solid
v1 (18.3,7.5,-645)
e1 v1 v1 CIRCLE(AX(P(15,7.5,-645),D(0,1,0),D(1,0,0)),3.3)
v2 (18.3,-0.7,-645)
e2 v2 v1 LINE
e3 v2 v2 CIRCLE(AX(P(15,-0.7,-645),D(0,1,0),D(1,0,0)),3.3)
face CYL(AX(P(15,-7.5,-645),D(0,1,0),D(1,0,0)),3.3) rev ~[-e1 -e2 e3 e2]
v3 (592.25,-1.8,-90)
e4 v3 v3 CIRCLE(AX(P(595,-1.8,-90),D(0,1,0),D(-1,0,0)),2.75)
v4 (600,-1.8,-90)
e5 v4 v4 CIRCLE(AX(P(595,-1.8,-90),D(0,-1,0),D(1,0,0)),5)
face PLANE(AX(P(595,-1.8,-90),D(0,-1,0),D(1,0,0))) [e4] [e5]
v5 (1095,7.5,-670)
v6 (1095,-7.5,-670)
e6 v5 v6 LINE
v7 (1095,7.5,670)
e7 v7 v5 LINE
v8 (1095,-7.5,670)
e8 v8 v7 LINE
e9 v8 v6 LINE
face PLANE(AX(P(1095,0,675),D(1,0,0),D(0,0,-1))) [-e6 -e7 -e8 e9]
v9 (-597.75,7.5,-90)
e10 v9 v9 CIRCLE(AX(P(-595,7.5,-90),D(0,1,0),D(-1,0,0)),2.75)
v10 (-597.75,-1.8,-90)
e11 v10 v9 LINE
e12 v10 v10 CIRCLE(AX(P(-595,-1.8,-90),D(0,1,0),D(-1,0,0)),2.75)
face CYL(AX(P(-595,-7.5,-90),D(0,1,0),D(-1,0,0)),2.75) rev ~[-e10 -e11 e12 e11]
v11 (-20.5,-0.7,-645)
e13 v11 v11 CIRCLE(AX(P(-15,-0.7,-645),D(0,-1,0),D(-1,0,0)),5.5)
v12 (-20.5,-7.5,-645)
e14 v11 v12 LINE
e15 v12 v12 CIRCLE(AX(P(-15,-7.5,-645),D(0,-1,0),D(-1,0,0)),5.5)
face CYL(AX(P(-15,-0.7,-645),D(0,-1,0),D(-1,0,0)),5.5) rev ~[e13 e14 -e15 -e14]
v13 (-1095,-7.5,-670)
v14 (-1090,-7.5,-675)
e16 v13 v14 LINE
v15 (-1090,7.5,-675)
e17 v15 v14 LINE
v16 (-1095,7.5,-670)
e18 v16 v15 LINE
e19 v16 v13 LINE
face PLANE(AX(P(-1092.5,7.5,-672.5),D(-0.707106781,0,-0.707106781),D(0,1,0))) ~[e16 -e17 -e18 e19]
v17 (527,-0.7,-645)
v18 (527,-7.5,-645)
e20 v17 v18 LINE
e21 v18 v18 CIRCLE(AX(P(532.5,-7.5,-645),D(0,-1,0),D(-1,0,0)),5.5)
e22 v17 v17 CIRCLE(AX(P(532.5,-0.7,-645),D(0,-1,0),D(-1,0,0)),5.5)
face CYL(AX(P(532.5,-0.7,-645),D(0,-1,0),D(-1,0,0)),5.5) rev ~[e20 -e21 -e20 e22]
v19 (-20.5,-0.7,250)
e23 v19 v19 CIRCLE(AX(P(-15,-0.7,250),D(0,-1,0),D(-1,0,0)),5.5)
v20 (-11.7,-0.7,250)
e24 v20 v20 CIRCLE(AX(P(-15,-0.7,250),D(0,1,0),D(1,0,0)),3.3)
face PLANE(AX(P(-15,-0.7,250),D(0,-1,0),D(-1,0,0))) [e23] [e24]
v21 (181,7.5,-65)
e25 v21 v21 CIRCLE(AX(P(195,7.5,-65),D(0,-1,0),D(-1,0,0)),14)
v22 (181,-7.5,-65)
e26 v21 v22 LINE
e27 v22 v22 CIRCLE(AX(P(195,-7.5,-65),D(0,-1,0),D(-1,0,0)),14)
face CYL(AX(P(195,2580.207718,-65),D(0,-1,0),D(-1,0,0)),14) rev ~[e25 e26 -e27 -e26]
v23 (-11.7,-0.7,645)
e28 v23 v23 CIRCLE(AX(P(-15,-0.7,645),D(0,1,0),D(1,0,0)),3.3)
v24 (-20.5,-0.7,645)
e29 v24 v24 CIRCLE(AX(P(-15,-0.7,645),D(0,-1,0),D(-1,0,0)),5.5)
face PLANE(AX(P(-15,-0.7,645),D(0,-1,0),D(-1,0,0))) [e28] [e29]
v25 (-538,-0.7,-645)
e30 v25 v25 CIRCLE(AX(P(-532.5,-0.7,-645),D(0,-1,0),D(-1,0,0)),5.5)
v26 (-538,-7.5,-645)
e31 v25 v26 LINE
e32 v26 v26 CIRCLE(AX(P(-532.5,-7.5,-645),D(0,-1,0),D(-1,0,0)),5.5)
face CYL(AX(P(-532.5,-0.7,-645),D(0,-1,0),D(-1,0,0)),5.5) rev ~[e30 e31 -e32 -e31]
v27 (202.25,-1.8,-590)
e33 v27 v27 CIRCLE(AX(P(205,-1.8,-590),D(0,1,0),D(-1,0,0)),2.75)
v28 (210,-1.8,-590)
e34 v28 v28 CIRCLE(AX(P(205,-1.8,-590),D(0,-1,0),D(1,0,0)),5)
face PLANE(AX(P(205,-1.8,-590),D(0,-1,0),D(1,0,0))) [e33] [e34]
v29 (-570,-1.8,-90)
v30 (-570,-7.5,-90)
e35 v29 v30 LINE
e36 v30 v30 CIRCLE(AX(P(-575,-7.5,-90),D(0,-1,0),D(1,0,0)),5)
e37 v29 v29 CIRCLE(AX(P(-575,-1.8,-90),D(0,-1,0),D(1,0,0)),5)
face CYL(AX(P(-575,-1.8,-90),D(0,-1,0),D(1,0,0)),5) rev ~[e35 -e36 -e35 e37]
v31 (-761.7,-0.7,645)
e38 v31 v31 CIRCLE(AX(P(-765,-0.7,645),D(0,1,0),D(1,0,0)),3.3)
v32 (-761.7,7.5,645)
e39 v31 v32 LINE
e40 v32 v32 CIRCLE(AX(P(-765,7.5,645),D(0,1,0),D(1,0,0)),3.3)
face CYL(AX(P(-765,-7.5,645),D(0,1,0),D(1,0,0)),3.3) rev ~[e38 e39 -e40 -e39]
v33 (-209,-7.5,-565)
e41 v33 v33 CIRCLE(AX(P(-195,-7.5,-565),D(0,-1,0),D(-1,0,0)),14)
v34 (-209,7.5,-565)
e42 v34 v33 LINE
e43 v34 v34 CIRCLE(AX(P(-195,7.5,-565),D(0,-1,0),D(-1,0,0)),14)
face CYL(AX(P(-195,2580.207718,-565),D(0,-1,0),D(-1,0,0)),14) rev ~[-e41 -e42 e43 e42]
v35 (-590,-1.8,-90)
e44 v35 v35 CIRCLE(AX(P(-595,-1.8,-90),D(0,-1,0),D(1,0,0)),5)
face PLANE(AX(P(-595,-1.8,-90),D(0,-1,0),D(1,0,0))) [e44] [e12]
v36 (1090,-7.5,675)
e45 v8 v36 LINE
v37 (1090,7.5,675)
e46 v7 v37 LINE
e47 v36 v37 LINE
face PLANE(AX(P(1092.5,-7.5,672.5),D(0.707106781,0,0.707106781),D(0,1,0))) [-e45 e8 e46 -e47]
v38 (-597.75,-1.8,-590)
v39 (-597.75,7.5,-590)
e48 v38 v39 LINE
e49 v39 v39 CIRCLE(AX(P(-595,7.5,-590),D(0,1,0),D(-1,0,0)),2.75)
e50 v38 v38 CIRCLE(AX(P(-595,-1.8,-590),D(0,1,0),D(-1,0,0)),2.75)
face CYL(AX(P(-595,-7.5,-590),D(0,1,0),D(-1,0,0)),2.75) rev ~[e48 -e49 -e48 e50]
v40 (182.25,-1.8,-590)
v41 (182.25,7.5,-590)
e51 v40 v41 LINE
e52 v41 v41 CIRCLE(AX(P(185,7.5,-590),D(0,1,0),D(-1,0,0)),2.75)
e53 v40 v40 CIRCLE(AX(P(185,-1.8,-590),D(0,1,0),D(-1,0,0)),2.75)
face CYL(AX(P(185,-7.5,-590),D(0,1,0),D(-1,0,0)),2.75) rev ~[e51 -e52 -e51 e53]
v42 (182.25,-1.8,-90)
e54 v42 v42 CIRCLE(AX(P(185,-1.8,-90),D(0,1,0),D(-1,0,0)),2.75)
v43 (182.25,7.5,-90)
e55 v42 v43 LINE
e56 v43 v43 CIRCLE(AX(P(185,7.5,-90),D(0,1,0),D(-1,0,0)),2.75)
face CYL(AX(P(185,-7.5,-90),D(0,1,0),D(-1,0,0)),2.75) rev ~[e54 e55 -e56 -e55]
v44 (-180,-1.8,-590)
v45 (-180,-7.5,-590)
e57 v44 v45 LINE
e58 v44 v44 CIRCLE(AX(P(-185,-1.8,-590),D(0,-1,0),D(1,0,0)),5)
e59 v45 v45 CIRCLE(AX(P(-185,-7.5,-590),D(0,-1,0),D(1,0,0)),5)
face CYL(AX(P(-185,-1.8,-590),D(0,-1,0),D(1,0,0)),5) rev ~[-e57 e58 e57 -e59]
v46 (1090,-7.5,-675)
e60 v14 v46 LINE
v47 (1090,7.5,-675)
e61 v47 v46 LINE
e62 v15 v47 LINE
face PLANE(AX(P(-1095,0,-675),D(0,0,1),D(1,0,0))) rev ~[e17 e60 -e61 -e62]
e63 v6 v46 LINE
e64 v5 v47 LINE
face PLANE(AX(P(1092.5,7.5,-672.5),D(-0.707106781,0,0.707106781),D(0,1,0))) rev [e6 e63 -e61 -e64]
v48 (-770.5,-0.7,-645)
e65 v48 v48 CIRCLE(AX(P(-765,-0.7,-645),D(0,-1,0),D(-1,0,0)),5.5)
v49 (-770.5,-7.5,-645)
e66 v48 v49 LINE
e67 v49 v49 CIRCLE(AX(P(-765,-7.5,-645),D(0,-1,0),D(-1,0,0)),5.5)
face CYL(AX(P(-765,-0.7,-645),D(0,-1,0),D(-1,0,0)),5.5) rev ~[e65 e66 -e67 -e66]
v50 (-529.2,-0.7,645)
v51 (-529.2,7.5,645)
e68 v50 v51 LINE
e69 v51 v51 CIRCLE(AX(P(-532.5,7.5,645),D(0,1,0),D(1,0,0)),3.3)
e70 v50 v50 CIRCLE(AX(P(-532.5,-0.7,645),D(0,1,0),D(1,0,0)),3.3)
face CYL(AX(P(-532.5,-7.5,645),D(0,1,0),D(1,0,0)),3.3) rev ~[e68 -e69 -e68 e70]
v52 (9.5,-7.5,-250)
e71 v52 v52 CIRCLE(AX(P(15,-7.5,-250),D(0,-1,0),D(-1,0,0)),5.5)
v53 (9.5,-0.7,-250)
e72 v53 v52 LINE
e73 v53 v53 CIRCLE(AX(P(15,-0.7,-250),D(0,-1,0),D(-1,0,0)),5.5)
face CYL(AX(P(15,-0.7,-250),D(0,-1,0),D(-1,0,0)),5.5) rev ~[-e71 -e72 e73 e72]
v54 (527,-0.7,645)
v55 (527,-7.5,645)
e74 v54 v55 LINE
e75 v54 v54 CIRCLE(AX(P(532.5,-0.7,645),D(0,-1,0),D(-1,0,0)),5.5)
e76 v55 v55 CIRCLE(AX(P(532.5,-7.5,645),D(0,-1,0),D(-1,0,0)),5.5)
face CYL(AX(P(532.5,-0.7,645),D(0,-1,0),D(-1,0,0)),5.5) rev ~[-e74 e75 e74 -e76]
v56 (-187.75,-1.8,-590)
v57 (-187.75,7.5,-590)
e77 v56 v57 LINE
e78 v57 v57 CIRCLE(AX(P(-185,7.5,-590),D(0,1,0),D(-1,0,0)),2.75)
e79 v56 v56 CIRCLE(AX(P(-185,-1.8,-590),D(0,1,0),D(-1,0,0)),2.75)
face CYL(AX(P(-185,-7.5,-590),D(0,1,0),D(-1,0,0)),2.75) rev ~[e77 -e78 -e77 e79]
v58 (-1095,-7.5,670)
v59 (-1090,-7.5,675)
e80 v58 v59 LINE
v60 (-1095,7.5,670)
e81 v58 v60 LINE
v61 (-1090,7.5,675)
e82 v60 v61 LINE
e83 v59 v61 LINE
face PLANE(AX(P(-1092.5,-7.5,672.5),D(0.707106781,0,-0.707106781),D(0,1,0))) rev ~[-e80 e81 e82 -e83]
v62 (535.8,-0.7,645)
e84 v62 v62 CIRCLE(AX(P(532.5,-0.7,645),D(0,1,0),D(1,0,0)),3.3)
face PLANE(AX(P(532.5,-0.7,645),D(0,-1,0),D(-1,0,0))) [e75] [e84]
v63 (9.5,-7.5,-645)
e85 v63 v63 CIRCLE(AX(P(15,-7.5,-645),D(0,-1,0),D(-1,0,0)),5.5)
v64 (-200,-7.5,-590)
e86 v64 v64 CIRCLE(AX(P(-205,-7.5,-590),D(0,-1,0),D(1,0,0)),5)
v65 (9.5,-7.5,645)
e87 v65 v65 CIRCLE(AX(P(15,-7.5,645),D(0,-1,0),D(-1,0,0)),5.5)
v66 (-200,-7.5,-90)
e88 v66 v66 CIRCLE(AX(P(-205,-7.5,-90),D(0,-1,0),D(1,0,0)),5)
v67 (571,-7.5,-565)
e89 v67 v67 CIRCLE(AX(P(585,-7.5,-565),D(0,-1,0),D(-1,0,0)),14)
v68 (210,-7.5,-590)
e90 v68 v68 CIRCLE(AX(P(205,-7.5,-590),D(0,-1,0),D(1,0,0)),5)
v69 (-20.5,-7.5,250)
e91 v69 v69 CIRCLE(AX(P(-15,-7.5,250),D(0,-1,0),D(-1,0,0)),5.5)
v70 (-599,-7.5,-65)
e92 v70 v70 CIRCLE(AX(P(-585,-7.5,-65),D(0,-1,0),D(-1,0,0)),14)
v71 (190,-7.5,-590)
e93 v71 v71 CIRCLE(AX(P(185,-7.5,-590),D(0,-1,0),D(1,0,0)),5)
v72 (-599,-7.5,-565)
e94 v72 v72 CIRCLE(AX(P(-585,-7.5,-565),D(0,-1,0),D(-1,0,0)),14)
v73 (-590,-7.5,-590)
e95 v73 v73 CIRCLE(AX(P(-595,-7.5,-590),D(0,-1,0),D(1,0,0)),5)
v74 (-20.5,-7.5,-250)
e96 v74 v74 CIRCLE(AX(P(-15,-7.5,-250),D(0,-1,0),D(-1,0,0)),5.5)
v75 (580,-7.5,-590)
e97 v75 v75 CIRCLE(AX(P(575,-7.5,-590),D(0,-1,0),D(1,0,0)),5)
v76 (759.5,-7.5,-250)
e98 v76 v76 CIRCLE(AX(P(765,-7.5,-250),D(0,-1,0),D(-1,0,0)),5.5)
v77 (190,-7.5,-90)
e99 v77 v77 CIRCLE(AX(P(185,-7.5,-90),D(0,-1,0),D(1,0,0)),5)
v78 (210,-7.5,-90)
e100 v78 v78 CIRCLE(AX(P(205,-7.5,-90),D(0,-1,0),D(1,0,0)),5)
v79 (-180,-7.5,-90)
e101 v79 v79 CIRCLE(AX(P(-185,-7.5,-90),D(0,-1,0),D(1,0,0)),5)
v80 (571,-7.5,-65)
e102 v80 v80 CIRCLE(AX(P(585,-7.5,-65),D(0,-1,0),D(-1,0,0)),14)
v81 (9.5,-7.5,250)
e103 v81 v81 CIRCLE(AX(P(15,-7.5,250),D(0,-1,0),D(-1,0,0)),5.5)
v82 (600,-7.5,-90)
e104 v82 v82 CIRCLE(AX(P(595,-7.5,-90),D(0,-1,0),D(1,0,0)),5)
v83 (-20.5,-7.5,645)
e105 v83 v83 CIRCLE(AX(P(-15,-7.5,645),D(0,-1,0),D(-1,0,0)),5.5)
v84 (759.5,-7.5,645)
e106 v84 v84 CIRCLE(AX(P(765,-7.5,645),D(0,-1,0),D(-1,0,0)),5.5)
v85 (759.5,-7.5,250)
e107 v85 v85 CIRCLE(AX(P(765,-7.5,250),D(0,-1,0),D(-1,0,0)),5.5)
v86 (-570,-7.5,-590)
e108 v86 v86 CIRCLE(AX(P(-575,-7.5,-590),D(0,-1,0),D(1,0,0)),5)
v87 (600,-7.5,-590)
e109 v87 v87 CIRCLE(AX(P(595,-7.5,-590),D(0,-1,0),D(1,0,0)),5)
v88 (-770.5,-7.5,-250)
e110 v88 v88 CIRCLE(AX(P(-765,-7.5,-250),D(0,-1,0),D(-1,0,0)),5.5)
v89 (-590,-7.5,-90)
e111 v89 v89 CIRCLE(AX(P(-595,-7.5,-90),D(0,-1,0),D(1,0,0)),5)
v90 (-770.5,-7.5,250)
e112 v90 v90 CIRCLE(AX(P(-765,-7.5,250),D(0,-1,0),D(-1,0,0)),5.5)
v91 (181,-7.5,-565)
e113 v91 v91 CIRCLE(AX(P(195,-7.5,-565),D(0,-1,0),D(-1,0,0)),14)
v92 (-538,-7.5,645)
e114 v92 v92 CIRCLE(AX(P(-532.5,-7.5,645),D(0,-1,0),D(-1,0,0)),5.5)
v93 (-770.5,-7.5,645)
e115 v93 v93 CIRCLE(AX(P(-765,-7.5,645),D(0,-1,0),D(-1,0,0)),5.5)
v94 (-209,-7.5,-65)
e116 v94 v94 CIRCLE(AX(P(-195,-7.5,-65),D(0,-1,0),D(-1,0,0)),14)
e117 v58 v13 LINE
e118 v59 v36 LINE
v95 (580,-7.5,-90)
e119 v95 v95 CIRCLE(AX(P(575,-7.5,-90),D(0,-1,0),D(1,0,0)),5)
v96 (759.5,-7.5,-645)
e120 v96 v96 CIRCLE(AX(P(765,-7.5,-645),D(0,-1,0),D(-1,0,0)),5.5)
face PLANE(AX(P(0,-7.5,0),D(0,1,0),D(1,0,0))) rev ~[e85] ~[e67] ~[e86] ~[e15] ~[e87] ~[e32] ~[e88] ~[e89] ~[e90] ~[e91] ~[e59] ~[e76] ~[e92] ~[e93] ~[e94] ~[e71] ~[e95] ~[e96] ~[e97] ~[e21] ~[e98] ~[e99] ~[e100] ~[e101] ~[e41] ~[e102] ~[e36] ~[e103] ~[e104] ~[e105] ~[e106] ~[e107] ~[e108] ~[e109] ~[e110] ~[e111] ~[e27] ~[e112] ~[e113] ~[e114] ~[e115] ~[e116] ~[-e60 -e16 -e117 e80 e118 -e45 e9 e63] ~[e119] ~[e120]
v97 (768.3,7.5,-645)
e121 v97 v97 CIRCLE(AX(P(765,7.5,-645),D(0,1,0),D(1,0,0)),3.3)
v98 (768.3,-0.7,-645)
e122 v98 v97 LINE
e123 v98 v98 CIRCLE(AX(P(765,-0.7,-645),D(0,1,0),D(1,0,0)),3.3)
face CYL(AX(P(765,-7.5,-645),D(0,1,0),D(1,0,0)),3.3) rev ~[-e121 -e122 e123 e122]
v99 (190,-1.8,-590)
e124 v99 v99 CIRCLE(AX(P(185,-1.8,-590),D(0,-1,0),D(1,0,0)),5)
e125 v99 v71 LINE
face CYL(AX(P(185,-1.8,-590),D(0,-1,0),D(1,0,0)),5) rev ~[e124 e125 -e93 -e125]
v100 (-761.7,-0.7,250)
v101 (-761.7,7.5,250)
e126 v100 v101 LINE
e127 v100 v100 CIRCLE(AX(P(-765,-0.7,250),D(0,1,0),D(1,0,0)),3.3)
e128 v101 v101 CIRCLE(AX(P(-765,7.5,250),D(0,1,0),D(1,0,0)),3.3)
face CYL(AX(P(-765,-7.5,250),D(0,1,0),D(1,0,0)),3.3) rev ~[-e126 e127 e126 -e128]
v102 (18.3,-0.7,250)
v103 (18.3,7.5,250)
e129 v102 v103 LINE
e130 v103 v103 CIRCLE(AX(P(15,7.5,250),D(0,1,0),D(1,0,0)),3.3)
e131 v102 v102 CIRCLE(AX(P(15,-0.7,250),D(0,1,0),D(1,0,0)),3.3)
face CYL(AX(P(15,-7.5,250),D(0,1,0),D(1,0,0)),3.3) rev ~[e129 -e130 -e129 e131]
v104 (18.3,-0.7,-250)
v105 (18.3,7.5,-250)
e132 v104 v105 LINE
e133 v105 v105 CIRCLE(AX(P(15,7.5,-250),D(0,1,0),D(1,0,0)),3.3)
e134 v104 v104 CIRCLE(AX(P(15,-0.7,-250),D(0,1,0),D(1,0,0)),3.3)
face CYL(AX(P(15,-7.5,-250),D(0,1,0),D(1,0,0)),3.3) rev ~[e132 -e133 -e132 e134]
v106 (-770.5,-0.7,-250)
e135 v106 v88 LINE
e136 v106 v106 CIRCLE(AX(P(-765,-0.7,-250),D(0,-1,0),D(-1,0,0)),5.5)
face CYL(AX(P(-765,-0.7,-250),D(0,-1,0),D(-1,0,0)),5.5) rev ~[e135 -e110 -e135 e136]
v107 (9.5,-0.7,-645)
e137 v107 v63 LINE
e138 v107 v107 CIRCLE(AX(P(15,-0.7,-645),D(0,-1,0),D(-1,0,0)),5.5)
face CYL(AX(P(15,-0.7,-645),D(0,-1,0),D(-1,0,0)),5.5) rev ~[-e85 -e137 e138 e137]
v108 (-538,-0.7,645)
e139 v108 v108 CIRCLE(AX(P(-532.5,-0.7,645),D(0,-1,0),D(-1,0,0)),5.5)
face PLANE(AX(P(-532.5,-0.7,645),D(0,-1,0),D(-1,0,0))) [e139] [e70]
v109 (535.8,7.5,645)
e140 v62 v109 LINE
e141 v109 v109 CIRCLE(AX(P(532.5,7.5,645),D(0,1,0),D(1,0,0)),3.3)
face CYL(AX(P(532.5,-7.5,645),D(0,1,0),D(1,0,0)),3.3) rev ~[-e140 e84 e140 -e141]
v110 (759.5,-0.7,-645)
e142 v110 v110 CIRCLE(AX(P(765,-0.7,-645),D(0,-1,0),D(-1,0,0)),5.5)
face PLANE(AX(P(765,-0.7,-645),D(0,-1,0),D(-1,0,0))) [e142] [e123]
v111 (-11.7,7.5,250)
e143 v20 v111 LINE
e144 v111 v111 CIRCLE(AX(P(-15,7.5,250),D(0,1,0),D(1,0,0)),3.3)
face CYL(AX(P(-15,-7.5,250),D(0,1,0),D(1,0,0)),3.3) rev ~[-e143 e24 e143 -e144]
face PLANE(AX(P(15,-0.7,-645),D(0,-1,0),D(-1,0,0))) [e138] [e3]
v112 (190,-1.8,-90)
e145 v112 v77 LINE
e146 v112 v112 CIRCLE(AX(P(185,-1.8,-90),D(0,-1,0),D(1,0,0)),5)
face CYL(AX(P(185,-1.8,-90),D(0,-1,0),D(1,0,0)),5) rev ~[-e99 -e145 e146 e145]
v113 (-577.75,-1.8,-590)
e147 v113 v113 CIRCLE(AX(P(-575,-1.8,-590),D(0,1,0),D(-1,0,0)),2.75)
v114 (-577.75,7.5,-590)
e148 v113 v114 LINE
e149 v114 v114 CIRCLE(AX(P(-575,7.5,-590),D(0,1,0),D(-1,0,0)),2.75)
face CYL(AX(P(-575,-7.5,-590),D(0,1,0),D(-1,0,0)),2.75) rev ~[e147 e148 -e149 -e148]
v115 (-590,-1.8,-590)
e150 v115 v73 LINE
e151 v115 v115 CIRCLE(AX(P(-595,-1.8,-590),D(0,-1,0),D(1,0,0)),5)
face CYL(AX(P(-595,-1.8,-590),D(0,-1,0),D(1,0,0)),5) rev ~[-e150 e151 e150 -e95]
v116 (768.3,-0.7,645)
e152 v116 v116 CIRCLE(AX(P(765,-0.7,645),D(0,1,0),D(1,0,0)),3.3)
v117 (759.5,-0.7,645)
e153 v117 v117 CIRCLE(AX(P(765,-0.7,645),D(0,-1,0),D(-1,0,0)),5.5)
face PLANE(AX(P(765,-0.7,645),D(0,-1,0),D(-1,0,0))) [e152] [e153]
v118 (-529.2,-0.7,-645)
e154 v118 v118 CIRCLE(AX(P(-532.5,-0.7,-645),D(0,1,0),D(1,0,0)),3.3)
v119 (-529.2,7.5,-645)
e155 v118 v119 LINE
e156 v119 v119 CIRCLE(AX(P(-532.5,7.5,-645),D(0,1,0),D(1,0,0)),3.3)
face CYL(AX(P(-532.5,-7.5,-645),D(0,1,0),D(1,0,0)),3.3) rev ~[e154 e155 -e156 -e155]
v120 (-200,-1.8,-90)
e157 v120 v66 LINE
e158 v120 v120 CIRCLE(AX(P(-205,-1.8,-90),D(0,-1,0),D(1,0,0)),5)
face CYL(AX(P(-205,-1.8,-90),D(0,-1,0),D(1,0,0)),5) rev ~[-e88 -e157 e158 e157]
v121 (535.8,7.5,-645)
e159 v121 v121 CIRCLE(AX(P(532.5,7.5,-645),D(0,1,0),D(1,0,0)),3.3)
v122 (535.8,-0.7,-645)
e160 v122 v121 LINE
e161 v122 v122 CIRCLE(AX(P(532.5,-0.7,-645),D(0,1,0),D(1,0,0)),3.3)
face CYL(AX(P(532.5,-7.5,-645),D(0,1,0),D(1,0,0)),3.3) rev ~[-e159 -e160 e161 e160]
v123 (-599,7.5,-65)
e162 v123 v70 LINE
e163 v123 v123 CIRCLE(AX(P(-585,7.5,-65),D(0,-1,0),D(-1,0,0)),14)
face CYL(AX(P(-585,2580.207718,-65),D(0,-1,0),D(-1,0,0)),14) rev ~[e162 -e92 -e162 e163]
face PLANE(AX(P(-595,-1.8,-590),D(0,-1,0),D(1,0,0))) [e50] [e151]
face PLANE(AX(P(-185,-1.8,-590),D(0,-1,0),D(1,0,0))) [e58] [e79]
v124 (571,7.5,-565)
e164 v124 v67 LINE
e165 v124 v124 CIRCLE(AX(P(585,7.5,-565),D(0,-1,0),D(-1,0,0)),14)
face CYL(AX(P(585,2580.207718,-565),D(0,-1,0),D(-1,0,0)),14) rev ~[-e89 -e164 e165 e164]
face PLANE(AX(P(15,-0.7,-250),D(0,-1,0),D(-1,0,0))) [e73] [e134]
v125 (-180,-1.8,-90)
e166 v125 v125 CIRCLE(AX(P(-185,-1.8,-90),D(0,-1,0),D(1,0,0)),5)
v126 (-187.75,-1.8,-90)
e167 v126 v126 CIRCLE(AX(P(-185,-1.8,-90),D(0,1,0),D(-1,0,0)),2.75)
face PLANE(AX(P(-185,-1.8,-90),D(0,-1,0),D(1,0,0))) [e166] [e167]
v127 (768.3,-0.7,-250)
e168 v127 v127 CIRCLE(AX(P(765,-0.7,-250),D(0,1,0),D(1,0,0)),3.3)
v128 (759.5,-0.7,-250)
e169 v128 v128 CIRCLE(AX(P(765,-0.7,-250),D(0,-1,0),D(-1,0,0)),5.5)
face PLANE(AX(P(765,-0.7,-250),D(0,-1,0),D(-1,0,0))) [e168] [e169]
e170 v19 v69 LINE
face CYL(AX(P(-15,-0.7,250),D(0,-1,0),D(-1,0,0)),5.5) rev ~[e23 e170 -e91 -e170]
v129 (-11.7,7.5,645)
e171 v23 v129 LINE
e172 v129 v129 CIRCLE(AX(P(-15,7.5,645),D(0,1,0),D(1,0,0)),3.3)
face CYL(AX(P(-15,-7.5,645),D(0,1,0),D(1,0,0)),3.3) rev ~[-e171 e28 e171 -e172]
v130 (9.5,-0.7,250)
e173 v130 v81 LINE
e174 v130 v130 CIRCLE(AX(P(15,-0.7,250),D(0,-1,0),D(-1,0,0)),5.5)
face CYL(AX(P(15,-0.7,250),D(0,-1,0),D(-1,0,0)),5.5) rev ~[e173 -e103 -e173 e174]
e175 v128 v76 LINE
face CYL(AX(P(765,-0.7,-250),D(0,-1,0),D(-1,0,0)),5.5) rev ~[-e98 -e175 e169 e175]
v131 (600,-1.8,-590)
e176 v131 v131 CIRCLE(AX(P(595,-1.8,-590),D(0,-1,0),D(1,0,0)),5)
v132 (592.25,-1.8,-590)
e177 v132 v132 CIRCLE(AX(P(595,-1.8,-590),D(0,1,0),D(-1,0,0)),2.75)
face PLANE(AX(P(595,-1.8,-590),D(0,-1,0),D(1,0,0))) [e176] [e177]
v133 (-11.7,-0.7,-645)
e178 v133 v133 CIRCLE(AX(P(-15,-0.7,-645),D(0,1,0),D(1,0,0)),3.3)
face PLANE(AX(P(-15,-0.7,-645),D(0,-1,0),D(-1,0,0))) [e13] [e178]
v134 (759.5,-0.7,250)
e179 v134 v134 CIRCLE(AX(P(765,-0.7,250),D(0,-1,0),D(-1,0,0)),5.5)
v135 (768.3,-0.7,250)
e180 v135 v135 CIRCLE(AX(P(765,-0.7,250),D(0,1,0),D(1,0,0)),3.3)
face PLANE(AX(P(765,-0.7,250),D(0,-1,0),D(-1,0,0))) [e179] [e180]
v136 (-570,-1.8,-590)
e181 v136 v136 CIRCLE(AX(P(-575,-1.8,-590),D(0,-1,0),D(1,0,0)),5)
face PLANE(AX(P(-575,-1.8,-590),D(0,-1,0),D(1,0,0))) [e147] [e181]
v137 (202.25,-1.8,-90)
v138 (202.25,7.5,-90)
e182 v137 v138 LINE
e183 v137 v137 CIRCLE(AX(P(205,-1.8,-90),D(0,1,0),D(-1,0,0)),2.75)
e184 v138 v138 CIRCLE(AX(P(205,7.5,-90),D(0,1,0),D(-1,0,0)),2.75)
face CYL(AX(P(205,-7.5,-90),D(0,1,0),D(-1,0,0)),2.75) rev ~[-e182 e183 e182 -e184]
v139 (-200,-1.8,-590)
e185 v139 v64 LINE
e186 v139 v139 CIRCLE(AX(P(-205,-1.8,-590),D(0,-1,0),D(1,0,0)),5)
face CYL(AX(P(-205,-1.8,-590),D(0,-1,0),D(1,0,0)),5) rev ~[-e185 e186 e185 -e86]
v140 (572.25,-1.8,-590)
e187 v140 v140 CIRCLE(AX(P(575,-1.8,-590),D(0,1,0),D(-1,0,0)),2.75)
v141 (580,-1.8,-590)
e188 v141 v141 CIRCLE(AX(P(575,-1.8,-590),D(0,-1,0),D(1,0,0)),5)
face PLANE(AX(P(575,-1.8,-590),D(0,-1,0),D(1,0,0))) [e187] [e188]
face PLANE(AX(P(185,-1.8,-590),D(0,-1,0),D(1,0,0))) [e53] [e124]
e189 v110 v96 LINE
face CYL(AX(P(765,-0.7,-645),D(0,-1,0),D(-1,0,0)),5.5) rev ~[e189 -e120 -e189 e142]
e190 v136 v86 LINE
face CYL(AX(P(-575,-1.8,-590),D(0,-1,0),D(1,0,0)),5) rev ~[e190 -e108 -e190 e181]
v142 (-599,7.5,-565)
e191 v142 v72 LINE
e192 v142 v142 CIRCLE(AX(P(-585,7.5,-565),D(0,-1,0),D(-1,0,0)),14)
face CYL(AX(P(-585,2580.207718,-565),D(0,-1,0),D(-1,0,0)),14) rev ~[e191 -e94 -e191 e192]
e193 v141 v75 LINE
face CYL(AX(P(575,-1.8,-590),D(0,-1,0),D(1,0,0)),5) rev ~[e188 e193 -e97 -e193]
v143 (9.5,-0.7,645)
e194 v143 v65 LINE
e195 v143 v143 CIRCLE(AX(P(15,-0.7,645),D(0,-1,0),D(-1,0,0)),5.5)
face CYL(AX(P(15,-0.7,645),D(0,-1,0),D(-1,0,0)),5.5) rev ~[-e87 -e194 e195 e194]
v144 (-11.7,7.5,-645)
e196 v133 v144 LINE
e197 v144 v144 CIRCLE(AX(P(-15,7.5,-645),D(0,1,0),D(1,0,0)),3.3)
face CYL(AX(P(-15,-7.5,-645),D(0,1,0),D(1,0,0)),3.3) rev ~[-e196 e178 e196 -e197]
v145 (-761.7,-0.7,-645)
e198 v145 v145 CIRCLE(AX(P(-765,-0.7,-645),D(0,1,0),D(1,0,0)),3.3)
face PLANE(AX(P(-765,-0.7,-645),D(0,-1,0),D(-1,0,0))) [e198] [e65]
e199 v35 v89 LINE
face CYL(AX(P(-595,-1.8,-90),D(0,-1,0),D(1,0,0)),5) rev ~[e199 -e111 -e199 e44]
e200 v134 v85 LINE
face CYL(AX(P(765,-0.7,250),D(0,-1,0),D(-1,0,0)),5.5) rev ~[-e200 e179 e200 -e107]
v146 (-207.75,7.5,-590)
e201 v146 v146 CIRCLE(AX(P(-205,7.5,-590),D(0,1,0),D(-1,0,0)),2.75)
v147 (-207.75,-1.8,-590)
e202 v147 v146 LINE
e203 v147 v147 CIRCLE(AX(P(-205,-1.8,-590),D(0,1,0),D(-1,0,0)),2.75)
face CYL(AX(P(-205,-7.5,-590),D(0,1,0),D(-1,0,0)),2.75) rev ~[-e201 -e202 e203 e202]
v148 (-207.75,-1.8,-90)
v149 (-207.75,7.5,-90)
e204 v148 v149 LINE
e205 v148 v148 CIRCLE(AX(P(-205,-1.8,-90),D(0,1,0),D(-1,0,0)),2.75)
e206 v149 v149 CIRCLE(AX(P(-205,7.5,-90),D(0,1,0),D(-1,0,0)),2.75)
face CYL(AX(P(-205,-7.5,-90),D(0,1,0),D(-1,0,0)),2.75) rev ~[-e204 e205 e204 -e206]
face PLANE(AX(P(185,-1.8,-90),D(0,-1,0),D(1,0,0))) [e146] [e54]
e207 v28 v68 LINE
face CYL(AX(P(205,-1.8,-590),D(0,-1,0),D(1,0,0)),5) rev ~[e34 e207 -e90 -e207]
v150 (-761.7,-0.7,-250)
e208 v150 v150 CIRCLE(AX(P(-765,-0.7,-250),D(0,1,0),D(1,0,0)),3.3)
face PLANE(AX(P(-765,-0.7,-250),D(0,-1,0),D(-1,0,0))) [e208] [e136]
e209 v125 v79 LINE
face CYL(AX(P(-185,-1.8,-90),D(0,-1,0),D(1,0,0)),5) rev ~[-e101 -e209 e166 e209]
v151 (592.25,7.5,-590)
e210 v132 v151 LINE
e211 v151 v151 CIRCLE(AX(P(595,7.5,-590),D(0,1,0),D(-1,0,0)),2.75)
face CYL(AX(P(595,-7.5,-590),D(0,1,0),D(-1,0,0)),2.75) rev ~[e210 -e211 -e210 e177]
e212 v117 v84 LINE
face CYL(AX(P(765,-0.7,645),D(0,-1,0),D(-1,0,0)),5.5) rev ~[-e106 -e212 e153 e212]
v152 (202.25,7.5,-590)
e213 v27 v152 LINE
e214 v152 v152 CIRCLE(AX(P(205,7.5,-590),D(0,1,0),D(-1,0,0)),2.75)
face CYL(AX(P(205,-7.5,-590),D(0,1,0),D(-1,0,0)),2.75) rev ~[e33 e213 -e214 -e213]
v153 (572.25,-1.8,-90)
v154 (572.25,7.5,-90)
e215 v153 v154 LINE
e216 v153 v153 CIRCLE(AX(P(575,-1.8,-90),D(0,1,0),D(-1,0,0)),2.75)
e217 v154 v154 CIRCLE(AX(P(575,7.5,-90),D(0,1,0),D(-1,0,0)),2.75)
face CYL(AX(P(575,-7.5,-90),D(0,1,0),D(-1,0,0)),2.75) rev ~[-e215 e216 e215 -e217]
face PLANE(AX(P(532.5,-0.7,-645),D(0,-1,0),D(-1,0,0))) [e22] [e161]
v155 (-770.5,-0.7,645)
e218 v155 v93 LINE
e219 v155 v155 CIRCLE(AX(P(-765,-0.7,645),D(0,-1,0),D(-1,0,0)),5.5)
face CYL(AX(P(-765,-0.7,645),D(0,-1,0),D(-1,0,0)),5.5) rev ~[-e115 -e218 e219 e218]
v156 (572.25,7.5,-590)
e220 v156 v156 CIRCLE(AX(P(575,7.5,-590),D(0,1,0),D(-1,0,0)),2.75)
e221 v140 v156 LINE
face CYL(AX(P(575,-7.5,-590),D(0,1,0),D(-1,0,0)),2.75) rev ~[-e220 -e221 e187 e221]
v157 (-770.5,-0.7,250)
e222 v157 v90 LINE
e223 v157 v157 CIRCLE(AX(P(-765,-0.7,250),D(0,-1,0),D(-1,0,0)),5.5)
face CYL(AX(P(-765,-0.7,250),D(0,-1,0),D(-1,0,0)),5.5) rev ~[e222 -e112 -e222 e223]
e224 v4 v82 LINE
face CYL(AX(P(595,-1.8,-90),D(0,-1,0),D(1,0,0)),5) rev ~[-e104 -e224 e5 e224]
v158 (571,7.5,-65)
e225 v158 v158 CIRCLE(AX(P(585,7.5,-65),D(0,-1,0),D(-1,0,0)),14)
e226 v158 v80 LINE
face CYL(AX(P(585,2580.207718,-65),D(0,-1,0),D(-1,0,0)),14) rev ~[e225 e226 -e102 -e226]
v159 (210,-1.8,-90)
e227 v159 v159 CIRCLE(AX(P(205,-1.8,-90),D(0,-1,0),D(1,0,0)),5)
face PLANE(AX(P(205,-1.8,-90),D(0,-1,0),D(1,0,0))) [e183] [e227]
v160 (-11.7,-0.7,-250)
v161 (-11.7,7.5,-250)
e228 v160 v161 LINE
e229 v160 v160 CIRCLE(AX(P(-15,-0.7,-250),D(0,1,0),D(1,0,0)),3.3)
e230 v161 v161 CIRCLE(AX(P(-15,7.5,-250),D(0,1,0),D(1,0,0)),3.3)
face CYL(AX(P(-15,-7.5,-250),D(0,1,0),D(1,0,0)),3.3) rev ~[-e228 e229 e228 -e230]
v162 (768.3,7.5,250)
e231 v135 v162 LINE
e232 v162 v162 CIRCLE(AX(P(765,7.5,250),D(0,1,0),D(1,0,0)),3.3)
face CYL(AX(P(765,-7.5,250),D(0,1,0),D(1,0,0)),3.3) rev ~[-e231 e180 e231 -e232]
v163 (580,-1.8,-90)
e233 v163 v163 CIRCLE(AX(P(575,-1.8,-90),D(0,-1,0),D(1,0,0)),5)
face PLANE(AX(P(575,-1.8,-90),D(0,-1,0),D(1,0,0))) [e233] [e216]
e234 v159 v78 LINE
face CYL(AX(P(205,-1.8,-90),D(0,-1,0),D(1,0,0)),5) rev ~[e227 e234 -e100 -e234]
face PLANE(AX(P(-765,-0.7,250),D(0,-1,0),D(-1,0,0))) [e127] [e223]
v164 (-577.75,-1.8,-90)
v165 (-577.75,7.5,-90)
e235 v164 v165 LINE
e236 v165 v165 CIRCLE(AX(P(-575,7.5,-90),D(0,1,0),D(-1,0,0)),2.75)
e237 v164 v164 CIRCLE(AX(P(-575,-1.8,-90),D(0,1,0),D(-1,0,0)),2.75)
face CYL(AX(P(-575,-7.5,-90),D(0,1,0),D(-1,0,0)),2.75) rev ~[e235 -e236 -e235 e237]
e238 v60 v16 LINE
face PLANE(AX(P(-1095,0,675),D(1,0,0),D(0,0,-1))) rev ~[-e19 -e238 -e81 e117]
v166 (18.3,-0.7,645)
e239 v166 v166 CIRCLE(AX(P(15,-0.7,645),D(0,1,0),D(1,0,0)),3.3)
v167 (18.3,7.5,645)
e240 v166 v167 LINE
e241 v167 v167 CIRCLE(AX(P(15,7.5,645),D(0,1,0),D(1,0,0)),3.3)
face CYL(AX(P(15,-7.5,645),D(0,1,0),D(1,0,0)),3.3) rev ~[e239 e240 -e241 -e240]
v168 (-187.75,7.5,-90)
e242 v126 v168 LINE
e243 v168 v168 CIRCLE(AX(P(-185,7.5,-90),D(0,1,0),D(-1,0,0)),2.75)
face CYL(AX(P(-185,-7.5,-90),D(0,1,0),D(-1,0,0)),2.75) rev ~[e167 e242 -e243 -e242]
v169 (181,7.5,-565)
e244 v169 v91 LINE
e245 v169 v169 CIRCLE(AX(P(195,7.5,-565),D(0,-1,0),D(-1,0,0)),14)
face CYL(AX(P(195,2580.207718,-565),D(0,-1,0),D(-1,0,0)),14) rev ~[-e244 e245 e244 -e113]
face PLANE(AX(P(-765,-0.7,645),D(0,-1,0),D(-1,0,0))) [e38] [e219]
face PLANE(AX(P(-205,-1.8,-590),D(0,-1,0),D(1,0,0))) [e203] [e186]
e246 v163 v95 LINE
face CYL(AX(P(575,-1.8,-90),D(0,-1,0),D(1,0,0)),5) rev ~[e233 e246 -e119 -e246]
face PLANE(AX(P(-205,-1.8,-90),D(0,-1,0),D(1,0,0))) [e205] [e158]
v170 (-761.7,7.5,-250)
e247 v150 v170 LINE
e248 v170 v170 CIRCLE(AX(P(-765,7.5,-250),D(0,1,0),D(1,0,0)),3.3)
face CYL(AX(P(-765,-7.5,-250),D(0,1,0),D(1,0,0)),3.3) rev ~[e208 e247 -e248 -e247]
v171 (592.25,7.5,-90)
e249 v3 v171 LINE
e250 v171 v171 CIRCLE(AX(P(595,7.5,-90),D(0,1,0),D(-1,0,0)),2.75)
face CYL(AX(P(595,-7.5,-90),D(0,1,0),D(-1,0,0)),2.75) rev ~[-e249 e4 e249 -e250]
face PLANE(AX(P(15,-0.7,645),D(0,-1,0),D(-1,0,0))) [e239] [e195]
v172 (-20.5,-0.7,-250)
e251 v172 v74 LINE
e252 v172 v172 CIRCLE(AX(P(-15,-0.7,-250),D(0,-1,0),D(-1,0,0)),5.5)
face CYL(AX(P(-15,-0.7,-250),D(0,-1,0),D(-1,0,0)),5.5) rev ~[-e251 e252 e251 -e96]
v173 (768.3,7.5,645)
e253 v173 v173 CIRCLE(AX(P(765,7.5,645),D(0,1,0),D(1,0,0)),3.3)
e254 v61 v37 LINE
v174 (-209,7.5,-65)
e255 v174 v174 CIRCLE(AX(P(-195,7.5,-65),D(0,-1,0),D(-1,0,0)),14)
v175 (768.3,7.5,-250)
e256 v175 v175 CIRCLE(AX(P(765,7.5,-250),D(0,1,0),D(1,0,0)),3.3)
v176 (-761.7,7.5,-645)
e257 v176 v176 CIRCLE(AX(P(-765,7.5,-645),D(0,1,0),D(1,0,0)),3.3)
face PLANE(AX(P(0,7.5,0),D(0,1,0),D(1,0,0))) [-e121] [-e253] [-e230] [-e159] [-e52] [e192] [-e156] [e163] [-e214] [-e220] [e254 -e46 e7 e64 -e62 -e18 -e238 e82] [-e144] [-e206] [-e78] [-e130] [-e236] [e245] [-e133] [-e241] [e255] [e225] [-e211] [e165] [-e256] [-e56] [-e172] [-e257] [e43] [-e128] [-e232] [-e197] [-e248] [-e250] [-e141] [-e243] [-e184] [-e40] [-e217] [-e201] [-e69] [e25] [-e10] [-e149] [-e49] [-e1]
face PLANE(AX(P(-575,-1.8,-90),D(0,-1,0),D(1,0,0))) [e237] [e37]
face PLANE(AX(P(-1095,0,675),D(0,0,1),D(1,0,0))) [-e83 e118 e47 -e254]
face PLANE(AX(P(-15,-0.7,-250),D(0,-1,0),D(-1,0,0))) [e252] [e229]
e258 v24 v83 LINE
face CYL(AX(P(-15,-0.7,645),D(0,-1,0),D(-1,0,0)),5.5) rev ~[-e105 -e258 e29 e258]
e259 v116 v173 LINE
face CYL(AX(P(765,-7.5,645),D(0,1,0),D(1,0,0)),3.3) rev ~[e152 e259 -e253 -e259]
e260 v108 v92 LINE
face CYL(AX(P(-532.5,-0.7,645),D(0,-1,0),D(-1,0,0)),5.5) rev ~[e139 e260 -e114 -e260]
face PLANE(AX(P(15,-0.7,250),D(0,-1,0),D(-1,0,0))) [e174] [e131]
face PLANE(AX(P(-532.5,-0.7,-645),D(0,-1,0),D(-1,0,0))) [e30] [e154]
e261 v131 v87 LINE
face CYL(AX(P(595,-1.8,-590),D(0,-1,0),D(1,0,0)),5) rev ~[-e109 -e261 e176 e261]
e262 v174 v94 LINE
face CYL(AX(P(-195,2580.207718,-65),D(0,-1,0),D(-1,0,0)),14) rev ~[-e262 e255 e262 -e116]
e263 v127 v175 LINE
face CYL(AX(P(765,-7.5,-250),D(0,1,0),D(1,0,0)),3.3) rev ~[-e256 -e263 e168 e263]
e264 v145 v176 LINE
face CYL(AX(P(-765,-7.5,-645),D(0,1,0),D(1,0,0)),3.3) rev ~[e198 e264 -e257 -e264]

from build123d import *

# Parameters (mm, degrees)
SKETCH_1_W                = 2190
SKETCH_1_H                = 1350
EXTRUDE_1_DEPTH           = 7.5
CHAMFER_1_SIZE            = 5
HOLE_WIZARD_25_0_25_1_D   = 28
HOLE_WIZARD_2_D           = 5.5
HOLE_WIZARD_2_CBORE_D     = 10
HOLE_WIZARD_2_CBORE_DEPTH = 5.7
HOLE_WIZARD_3_D           = 6.6
HOLE_WIZARD_3_CBORE_D     = 11
HOLE_WIZARD_3_CBORE_DEPTH = 6.8


with BuildPart() as part:
    # 草图1 → 凸台-拉伸1 (new, symmetric)
    with BuildSketch(Plane(origin=(0, 0, 0), x_dir=(1, 0, 0), z_dir=(0, 1, 0))):
        Rectangle(SKETCH_1_W, SKETCH_1_H)
    extrude(amount=EXTRUDE_1_DEPTH, both=True)

    # 倒角1
    chamfer_1_edges = [part.edges().sort_by_distance(p)[0] for p in [
        (1095, 0, 675),
        (-1095, 0, 675),
        (-1095, 0, -675),
        (1095, 0, -675),
    ]]
    chamfer(chamfer_1_edges, length=CHAMFER_1_SIZE)

    # Ø25.0 (25) 直径孔1 (through all)
    with Locations(Plane(origin=(0, 7.5, 0), x_dir=(1, 0, 0), z_dir=(0, 1, 0))):
        with Locations((-585, 565), (-195, 565), (195, 565), (585, 565), (-585, 65), (-195, 65), (195, 65), (585, 65)):
            Hole(HOLE_WIZARD_25_0_25_1_D / 2)

    # 打孔尺寸(%根据)内六角圆柱头螺钉的类型2 (through all)
    with Locations(Plane.XZ.offset(7.5)):
        with Locations((-595, -590), (-575, -590), (-205, -590), (-185, -590), (185, -590), (205, -590), (575, -590), (595, -590), (-205, -90), (-185, -90), (185, -90), (205, -90), (575, -90), (595, -90), (-595, -90), (-575, -90)):
            CounterBoreHole(HOLE_WIZARD_2_D / 2, HOLE_WIZARD_2_CBORE_D / 2, HOLE_WIZARD_2_CBORE_DEPTH)

    # 打孔尺寸(%根据)内六角圆柱头螺钉的类型3 (through all)
    with Locations(Plane(origin=(0, -7.5, 0), x_dir=(-1, 0, 0), z_dir=(0, -1, 0))):
        with Locations((-765, 645), (-532.5, 645), (-765, 250), (15, 645), (15, 250), (765, 250), (532.5, 645), (765, 645), (765, -645), (532.5, -645), (765, -250), (15, -250), (15, -645), (-765, -250), (-532.5, -645), (-765, -645), (-15, -645), (-15, -250), (-15, 250), (-15, 645)):
            CounterBoreHole(HOLE_WIZARD_3_D / 2, HOLE_WIZARD_3_CBORE_D / 2, HOLE_WIZARD_3_CBORE_DEPTH)


solid = part.part
